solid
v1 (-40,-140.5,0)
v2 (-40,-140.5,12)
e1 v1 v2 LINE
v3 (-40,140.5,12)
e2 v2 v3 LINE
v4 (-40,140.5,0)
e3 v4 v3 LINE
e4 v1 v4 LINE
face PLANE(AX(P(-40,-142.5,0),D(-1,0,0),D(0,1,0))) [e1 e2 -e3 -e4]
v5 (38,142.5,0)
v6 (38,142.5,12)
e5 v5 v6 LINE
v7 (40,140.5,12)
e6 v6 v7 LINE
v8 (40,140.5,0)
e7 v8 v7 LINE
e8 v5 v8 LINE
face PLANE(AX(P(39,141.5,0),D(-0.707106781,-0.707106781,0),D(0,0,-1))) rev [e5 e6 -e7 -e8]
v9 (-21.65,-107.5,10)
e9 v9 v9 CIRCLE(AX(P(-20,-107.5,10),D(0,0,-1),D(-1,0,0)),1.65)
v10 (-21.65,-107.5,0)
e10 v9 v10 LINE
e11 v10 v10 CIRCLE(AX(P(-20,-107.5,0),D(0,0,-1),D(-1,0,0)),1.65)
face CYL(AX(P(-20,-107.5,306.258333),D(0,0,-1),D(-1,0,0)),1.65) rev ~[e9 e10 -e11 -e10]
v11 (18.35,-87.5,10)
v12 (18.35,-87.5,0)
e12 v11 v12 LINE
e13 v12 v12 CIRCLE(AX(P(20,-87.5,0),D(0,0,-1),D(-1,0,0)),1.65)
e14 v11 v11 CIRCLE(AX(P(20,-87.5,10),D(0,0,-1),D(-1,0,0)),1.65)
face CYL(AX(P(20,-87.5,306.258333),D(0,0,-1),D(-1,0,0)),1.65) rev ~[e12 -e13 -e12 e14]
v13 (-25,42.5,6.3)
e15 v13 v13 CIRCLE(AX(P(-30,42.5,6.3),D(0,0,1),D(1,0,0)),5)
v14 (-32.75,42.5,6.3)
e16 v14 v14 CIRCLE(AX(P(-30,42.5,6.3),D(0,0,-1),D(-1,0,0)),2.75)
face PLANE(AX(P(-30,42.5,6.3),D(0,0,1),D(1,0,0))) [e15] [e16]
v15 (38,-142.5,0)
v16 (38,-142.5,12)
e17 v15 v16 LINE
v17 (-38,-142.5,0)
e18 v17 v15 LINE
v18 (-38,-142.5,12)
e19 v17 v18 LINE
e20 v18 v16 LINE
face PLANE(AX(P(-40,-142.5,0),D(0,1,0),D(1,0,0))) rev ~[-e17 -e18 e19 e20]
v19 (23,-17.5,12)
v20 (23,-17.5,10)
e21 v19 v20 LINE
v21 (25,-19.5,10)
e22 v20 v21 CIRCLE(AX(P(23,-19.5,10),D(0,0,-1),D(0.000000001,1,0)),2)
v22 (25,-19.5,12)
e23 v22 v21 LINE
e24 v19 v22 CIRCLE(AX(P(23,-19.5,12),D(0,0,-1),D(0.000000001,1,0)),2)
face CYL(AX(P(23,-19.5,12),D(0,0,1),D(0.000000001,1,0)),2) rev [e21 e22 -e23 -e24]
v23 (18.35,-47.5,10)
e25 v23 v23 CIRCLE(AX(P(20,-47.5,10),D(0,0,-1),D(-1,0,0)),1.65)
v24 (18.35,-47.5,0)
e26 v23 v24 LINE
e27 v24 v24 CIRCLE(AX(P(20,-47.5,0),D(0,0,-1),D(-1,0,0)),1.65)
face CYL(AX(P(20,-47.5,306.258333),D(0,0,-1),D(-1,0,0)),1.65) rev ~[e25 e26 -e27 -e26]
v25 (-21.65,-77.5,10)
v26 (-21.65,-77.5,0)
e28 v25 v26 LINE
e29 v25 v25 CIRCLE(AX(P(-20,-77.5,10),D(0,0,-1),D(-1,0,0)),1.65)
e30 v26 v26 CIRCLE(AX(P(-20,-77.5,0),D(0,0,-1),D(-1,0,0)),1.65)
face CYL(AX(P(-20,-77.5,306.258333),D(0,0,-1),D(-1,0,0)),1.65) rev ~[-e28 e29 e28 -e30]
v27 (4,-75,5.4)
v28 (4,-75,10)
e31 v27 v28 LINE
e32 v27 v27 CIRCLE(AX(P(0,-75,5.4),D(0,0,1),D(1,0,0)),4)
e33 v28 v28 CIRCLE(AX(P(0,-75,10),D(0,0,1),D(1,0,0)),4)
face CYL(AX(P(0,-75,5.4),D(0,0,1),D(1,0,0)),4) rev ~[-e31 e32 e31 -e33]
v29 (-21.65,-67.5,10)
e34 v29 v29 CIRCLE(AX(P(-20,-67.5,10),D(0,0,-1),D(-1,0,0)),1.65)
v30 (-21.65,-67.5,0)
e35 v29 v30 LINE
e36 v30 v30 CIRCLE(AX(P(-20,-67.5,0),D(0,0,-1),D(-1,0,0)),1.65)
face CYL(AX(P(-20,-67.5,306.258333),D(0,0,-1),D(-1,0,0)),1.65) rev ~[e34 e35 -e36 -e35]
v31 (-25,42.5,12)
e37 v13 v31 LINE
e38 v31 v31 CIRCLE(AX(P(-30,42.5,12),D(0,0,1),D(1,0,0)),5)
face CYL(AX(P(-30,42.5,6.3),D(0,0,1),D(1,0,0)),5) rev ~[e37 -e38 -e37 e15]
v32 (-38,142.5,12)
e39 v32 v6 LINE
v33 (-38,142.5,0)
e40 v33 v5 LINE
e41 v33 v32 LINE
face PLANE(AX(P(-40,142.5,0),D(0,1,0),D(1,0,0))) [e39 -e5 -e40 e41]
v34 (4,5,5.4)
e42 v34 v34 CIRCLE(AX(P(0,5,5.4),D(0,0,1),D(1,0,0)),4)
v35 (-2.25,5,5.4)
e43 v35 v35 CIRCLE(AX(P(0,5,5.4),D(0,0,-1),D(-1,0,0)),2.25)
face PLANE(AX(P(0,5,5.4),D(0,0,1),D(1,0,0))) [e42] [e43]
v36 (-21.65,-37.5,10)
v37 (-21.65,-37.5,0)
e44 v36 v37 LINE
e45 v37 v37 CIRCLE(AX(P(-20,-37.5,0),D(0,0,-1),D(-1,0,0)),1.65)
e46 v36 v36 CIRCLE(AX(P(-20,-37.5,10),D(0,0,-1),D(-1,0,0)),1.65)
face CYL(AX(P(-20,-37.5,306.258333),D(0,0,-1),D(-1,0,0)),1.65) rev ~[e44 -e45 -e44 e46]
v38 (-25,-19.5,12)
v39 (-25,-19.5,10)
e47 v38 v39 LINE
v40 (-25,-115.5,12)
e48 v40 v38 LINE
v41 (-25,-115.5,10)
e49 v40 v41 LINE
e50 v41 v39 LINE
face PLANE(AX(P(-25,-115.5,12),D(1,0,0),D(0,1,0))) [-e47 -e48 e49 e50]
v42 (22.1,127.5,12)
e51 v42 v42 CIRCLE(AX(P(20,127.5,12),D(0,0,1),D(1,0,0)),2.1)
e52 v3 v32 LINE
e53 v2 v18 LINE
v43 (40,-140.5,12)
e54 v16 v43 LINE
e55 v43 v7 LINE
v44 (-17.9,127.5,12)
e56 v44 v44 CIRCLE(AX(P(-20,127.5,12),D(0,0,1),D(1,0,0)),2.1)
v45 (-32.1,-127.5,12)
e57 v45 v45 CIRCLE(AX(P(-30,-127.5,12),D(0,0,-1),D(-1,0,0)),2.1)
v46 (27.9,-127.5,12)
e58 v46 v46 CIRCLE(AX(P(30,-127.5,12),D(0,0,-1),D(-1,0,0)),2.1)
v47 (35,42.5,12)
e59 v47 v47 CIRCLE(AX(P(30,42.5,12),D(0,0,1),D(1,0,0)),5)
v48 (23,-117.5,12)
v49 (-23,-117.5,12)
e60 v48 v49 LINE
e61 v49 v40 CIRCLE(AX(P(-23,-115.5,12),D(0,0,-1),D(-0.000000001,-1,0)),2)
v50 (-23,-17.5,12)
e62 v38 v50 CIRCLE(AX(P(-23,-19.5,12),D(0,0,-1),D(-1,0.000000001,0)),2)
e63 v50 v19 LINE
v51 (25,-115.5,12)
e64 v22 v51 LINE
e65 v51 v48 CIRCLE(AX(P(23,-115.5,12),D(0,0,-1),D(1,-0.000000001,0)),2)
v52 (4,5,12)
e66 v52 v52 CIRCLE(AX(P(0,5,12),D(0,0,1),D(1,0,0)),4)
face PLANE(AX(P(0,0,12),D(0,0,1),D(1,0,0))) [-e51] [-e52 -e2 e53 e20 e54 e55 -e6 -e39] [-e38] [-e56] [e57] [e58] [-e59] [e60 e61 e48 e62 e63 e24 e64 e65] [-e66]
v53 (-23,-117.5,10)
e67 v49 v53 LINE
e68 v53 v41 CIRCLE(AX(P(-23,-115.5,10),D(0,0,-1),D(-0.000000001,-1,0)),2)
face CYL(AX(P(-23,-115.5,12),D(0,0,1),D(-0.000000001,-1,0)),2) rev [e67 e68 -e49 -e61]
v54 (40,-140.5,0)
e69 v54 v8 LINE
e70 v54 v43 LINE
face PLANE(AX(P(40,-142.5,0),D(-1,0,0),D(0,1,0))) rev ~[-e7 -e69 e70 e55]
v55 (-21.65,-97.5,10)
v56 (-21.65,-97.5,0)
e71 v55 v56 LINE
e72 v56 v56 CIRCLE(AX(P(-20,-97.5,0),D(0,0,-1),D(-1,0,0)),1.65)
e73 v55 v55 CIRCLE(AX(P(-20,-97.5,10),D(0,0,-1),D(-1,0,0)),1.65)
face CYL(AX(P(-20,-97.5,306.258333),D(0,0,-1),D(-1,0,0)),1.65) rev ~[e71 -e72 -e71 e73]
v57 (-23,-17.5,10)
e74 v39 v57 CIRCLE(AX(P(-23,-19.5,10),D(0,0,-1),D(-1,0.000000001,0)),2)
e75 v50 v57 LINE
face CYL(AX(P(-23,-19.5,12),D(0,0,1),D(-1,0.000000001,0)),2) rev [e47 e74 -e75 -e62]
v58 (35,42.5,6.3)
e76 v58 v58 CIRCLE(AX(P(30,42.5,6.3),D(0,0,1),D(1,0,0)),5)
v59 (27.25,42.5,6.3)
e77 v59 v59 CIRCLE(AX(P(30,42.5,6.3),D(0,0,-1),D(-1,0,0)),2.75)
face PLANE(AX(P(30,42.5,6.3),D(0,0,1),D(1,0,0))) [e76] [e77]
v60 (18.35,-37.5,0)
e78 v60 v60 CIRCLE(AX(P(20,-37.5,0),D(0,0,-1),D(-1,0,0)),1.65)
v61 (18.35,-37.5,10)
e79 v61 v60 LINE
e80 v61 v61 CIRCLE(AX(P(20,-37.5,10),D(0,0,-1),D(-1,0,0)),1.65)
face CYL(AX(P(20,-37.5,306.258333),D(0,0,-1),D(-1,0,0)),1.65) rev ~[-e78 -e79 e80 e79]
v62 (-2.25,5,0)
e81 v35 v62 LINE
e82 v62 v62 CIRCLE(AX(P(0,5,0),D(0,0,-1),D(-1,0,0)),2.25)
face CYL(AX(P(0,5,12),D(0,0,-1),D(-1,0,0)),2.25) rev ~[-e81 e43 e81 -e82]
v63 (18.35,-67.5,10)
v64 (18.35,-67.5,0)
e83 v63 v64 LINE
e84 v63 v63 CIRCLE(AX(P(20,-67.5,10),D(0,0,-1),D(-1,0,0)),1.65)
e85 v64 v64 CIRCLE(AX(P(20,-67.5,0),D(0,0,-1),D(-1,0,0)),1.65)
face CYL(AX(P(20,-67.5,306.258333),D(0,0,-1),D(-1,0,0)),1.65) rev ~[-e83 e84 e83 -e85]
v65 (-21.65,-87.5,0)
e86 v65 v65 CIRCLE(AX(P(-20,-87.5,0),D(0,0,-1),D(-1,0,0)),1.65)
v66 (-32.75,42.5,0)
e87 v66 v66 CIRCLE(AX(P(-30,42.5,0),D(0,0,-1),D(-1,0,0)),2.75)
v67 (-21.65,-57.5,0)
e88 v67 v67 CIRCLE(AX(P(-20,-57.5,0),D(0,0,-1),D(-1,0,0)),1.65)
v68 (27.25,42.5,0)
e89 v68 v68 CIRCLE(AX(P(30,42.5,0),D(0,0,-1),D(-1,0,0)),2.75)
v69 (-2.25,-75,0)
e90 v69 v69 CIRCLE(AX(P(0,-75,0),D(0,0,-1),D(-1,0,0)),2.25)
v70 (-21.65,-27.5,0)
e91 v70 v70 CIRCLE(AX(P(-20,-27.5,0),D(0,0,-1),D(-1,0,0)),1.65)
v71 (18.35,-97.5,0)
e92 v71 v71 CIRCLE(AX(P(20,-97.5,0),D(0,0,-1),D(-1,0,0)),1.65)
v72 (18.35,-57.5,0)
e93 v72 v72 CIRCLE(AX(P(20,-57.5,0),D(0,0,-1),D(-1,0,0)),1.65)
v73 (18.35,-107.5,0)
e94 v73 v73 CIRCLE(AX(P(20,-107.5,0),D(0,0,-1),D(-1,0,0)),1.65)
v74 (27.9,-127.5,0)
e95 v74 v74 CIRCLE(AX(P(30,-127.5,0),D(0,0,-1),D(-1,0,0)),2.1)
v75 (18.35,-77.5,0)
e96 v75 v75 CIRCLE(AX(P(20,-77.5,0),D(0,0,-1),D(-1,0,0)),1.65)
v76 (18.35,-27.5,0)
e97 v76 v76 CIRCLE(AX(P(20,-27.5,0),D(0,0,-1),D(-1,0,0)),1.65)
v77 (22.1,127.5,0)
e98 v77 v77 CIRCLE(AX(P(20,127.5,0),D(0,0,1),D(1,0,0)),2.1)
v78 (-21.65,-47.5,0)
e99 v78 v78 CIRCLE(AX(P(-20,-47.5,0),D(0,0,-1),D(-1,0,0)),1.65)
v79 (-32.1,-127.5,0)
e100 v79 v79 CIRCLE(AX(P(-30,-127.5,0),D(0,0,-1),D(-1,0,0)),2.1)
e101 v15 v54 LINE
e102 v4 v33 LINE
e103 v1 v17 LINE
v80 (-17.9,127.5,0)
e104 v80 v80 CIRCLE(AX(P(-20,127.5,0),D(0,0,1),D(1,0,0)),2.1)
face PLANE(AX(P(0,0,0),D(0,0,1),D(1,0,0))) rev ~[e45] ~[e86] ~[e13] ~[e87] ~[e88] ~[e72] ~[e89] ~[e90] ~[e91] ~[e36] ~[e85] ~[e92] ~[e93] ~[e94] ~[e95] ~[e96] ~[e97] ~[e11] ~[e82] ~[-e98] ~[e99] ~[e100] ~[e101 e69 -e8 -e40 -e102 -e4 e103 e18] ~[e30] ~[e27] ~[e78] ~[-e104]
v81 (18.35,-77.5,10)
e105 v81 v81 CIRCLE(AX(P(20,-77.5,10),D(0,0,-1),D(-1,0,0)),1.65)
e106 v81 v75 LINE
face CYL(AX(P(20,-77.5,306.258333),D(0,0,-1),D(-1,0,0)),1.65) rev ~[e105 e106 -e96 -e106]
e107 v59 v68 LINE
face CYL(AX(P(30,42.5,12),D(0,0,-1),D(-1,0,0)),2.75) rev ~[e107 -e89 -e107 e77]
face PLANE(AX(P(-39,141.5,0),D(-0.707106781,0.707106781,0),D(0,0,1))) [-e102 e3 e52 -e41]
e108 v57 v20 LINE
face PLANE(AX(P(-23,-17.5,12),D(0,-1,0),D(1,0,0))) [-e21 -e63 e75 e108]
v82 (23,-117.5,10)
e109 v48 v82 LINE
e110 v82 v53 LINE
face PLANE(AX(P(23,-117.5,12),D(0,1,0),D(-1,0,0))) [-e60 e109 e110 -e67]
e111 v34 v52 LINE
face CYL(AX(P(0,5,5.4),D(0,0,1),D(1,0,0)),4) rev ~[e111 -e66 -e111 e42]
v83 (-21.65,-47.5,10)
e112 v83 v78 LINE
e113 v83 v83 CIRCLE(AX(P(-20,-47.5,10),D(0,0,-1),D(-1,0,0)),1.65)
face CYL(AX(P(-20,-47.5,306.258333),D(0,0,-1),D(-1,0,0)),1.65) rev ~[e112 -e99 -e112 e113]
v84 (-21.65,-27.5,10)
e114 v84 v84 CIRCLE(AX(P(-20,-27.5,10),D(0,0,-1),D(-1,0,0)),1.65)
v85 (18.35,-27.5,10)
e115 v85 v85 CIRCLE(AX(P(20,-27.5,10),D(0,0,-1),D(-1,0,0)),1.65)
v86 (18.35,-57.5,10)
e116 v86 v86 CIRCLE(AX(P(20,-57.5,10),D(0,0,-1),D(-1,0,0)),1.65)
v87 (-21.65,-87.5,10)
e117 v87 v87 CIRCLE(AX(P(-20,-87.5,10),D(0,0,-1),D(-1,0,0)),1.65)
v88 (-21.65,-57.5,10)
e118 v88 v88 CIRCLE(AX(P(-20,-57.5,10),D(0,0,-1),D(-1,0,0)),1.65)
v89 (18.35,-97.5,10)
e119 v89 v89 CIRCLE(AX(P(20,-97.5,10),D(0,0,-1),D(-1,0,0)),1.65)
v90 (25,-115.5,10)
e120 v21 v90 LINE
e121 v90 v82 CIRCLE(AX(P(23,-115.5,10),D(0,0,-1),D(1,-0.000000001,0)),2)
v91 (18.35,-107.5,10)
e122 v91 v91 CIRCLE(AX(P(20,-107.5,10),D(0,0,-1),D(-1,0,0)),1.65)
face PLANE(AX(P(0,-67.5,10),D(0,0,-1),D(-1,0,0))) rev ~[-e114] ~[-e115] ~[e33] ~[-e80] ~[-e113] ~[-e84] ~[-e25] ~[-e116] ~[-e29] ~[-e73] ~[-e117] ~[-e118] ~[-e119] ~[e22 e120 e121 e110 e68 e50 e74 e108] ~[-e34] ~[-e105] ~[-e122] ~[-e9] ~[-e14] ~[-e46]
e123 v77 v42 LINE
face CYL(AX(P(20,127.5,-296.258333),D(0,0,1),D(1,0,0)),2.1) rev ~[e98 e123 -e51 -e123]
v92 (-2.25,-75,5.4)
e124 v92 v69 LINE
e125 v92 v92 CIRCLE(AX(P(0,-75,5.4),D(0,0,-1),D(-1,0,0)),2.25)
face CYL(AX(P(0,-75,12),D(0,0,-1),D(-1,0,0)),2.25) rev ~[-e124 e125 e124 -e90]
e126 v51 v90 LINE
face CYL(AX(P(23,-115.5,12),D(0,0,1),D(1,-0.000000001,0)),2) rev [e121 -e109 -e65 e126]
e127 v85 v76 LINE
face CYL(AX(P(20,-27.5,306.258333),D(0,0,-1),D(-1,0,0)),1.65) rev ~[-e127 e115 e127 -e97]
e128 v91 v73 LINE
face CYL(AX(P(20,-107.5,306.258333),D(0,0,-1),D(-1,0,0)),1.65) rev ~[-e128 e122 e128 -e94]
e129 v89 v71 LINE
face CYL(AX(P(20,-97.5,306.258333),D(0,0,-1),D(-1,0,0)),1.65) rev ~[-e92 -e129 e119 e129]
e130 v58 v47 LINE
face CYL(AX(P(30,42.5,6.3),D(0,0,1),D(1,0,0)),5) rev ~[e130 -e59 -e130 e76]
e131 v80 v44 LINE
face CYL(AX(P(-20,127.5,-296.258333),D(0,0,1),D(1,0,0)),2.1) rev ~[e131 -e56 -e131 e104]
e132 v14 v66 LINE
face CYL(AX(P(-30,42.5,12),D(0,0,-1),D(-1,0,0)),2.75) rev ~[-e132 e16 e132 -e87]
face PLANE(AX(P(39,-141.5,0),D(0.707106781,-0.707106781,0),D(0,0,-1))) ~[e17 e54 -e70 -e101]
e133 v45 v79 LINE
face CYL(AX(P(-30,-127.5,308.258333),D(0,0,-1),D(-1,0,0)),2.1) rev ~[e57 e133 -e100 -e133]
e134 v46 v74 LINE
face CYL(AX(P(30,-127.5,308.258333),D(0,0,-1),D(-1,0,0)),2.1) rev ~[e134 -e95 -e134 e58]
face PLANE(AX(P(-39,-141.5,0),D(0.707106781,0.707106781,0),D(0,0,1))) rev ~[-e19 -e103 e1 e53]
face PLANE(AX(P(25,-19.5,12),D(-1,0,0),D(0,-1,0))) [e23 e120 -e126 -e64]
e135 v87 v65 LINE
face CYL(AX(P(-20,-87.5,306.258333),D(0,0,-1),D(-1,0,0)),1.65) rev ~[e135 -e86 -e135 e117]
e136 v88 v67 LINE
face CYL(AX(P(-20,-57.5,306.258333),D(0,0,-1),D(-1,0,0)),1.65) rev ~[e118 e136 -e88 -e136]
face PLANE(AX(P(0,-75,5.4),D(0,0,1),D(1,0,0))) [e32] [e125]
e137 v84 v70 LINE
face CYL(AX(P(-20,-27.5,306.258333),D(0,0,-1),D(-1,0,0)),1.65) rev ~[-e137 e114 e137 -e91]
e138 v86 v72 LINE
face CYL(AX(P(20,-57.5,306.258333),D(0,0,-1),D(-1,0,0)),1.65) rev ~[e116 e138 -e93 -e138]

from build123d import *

# Parameters (mm, degrees)
SKETCH_1_W                = 80
SKETCH_1_H                = 285
EXTRUDE_1_DEPTH           = 12
HOLE_WIZARD_1_D           = 5.5
HOLE_WIZARD_1_CBORE_D     = 10
HOLE_WIZARD_1_CBORE_DEPTH = 5.7
HOLE_WIZARD_M5_1_D        = 4.2
CUT_EXTRUDE_2_DEPTH       = 2
HOLE_WIZARD_M4_1_D        = 3.3
HOLE_WIZARD_M5_2_D        = 4.2
CHAMFER_2_SIZE            = 2
HOLE_WIZARD_2_D           = 4.5
HOLE_WIZARD_2_CBORE_D     = 8
HOLE_WIZARD_2_CBORE_DEPTH = 6.6


with BuildPart() as part:
    # 草图1 → 凸台-拉伸1 (new body)
    with BuildSketch(Plane.XY):
        Rectangle(SKETCH_1_W, SKETCH_1_H)
    extrude(amount=EXTRUDE_1_DEPTH)

    # 打孔尺寸(%根据)内六角圆柱头螺钉的类型1 (through all)
    with Locations(Plane.XY.offset(12)):
        with Locations((30, 42.5), (-30, 42.5)):
            CounterBoreHole(HOLE_WIZARD_1_D / 2, HOLE_WIZARD_1_CBORE_D / 2, HOLE_WIZARD_1_CBORE_DEPTH)

    # M5 螺纹孔1 (through all)
    with Locations(Plane(origin=(0, 0, 0), x_dir=(-1, 0, 0), z_dir=(0, 0, -1))):
        with Locations((-20, 127.5), (20, 127.5)):
            Hole(HOLE_WIZARD_M5_1_D / 2)

    # 草图25 → 切除-拉伸2 (cut)
    with BuildSketch(Plane.XY.offset(12)):
        with BuildLine():
            Line((-23, -17.5), (23, -17.5))
            ThreePointArc((23, -17.5), (24.414213562, -18.085786438), (25, -19.5))
            Line((25, -19.5), (25, -115.5))
            ThreePointArc((25, -115.5), (24.414213562, -116.914213562), (23, -117.5))
            Line((23, -117.5), (-23, -117.5))
            ThreePointArc((-23, -117.5), (-24.414213562, -116.914213562), (-25, -115.5))
            Line((-25, -115.5), (-25, -19.5))
            ThreePointArc((-25, -19.5), (-24.414213562, -18.085786438), (-23, -17.5))
        make_face()
    extrude(amount=-CUT_EXTRUDE_2_DEPTH, mode=Mode.SUBTRACT)

    # M4 螺纹孔1 (through all)
    with Locations(Plane.XY.offset(10)):
        with Locations((-20, -27.5), (20, -27.5), (20, -37.5), (20, -47.5), (-20, -37.5), (-20, -47.5), (-20, -57.5), (20, -57.5), (-20, -67.5), (20, -67.5), (-20, -77.5), (20, -77.5), (-20, -87.5), (20, -87.5), (-20, -97.5), (20, -97.5), (-20, -107.5), (20, -107.5)):
            Hole(HOLE_WIZARD_M4_1_D / 2)

    # M5 螺纹孔2 (through all)
    with Locations(Plane.XY.offset(12)):
        with Locations((-30, -127.5), (30, -127.5)):
            Hole(HOLE_WIZARD_M5_2_D / 2)

    # 倒角2
    chamfer_2_edges = [part.edges().sort_by_distance(p)[0] for p in [
        (40, -142.5, 6),
        (-40, -142.5, 6),
        (-40, 142.5, 6),
        (40, 142.5, 6),
    ]]
    chamfer(chamfer_2_edges, length=CHAMFER_2_SIZE)

    # 打孔尺寸(%根据)内六角圆柱头螺钉的类型2 (through all)
    with Locations(Plane.XY.offset(12)):
        with Locations((0, 5), (0, -75)):
            CounterBoreHole(HOLE_WIZARD_2_D / 2, HOLE_WIZARD_2_CBORE_D / 2, HOLE_WIZARD_2_CBORE_DEPTH)


solid = part.part
